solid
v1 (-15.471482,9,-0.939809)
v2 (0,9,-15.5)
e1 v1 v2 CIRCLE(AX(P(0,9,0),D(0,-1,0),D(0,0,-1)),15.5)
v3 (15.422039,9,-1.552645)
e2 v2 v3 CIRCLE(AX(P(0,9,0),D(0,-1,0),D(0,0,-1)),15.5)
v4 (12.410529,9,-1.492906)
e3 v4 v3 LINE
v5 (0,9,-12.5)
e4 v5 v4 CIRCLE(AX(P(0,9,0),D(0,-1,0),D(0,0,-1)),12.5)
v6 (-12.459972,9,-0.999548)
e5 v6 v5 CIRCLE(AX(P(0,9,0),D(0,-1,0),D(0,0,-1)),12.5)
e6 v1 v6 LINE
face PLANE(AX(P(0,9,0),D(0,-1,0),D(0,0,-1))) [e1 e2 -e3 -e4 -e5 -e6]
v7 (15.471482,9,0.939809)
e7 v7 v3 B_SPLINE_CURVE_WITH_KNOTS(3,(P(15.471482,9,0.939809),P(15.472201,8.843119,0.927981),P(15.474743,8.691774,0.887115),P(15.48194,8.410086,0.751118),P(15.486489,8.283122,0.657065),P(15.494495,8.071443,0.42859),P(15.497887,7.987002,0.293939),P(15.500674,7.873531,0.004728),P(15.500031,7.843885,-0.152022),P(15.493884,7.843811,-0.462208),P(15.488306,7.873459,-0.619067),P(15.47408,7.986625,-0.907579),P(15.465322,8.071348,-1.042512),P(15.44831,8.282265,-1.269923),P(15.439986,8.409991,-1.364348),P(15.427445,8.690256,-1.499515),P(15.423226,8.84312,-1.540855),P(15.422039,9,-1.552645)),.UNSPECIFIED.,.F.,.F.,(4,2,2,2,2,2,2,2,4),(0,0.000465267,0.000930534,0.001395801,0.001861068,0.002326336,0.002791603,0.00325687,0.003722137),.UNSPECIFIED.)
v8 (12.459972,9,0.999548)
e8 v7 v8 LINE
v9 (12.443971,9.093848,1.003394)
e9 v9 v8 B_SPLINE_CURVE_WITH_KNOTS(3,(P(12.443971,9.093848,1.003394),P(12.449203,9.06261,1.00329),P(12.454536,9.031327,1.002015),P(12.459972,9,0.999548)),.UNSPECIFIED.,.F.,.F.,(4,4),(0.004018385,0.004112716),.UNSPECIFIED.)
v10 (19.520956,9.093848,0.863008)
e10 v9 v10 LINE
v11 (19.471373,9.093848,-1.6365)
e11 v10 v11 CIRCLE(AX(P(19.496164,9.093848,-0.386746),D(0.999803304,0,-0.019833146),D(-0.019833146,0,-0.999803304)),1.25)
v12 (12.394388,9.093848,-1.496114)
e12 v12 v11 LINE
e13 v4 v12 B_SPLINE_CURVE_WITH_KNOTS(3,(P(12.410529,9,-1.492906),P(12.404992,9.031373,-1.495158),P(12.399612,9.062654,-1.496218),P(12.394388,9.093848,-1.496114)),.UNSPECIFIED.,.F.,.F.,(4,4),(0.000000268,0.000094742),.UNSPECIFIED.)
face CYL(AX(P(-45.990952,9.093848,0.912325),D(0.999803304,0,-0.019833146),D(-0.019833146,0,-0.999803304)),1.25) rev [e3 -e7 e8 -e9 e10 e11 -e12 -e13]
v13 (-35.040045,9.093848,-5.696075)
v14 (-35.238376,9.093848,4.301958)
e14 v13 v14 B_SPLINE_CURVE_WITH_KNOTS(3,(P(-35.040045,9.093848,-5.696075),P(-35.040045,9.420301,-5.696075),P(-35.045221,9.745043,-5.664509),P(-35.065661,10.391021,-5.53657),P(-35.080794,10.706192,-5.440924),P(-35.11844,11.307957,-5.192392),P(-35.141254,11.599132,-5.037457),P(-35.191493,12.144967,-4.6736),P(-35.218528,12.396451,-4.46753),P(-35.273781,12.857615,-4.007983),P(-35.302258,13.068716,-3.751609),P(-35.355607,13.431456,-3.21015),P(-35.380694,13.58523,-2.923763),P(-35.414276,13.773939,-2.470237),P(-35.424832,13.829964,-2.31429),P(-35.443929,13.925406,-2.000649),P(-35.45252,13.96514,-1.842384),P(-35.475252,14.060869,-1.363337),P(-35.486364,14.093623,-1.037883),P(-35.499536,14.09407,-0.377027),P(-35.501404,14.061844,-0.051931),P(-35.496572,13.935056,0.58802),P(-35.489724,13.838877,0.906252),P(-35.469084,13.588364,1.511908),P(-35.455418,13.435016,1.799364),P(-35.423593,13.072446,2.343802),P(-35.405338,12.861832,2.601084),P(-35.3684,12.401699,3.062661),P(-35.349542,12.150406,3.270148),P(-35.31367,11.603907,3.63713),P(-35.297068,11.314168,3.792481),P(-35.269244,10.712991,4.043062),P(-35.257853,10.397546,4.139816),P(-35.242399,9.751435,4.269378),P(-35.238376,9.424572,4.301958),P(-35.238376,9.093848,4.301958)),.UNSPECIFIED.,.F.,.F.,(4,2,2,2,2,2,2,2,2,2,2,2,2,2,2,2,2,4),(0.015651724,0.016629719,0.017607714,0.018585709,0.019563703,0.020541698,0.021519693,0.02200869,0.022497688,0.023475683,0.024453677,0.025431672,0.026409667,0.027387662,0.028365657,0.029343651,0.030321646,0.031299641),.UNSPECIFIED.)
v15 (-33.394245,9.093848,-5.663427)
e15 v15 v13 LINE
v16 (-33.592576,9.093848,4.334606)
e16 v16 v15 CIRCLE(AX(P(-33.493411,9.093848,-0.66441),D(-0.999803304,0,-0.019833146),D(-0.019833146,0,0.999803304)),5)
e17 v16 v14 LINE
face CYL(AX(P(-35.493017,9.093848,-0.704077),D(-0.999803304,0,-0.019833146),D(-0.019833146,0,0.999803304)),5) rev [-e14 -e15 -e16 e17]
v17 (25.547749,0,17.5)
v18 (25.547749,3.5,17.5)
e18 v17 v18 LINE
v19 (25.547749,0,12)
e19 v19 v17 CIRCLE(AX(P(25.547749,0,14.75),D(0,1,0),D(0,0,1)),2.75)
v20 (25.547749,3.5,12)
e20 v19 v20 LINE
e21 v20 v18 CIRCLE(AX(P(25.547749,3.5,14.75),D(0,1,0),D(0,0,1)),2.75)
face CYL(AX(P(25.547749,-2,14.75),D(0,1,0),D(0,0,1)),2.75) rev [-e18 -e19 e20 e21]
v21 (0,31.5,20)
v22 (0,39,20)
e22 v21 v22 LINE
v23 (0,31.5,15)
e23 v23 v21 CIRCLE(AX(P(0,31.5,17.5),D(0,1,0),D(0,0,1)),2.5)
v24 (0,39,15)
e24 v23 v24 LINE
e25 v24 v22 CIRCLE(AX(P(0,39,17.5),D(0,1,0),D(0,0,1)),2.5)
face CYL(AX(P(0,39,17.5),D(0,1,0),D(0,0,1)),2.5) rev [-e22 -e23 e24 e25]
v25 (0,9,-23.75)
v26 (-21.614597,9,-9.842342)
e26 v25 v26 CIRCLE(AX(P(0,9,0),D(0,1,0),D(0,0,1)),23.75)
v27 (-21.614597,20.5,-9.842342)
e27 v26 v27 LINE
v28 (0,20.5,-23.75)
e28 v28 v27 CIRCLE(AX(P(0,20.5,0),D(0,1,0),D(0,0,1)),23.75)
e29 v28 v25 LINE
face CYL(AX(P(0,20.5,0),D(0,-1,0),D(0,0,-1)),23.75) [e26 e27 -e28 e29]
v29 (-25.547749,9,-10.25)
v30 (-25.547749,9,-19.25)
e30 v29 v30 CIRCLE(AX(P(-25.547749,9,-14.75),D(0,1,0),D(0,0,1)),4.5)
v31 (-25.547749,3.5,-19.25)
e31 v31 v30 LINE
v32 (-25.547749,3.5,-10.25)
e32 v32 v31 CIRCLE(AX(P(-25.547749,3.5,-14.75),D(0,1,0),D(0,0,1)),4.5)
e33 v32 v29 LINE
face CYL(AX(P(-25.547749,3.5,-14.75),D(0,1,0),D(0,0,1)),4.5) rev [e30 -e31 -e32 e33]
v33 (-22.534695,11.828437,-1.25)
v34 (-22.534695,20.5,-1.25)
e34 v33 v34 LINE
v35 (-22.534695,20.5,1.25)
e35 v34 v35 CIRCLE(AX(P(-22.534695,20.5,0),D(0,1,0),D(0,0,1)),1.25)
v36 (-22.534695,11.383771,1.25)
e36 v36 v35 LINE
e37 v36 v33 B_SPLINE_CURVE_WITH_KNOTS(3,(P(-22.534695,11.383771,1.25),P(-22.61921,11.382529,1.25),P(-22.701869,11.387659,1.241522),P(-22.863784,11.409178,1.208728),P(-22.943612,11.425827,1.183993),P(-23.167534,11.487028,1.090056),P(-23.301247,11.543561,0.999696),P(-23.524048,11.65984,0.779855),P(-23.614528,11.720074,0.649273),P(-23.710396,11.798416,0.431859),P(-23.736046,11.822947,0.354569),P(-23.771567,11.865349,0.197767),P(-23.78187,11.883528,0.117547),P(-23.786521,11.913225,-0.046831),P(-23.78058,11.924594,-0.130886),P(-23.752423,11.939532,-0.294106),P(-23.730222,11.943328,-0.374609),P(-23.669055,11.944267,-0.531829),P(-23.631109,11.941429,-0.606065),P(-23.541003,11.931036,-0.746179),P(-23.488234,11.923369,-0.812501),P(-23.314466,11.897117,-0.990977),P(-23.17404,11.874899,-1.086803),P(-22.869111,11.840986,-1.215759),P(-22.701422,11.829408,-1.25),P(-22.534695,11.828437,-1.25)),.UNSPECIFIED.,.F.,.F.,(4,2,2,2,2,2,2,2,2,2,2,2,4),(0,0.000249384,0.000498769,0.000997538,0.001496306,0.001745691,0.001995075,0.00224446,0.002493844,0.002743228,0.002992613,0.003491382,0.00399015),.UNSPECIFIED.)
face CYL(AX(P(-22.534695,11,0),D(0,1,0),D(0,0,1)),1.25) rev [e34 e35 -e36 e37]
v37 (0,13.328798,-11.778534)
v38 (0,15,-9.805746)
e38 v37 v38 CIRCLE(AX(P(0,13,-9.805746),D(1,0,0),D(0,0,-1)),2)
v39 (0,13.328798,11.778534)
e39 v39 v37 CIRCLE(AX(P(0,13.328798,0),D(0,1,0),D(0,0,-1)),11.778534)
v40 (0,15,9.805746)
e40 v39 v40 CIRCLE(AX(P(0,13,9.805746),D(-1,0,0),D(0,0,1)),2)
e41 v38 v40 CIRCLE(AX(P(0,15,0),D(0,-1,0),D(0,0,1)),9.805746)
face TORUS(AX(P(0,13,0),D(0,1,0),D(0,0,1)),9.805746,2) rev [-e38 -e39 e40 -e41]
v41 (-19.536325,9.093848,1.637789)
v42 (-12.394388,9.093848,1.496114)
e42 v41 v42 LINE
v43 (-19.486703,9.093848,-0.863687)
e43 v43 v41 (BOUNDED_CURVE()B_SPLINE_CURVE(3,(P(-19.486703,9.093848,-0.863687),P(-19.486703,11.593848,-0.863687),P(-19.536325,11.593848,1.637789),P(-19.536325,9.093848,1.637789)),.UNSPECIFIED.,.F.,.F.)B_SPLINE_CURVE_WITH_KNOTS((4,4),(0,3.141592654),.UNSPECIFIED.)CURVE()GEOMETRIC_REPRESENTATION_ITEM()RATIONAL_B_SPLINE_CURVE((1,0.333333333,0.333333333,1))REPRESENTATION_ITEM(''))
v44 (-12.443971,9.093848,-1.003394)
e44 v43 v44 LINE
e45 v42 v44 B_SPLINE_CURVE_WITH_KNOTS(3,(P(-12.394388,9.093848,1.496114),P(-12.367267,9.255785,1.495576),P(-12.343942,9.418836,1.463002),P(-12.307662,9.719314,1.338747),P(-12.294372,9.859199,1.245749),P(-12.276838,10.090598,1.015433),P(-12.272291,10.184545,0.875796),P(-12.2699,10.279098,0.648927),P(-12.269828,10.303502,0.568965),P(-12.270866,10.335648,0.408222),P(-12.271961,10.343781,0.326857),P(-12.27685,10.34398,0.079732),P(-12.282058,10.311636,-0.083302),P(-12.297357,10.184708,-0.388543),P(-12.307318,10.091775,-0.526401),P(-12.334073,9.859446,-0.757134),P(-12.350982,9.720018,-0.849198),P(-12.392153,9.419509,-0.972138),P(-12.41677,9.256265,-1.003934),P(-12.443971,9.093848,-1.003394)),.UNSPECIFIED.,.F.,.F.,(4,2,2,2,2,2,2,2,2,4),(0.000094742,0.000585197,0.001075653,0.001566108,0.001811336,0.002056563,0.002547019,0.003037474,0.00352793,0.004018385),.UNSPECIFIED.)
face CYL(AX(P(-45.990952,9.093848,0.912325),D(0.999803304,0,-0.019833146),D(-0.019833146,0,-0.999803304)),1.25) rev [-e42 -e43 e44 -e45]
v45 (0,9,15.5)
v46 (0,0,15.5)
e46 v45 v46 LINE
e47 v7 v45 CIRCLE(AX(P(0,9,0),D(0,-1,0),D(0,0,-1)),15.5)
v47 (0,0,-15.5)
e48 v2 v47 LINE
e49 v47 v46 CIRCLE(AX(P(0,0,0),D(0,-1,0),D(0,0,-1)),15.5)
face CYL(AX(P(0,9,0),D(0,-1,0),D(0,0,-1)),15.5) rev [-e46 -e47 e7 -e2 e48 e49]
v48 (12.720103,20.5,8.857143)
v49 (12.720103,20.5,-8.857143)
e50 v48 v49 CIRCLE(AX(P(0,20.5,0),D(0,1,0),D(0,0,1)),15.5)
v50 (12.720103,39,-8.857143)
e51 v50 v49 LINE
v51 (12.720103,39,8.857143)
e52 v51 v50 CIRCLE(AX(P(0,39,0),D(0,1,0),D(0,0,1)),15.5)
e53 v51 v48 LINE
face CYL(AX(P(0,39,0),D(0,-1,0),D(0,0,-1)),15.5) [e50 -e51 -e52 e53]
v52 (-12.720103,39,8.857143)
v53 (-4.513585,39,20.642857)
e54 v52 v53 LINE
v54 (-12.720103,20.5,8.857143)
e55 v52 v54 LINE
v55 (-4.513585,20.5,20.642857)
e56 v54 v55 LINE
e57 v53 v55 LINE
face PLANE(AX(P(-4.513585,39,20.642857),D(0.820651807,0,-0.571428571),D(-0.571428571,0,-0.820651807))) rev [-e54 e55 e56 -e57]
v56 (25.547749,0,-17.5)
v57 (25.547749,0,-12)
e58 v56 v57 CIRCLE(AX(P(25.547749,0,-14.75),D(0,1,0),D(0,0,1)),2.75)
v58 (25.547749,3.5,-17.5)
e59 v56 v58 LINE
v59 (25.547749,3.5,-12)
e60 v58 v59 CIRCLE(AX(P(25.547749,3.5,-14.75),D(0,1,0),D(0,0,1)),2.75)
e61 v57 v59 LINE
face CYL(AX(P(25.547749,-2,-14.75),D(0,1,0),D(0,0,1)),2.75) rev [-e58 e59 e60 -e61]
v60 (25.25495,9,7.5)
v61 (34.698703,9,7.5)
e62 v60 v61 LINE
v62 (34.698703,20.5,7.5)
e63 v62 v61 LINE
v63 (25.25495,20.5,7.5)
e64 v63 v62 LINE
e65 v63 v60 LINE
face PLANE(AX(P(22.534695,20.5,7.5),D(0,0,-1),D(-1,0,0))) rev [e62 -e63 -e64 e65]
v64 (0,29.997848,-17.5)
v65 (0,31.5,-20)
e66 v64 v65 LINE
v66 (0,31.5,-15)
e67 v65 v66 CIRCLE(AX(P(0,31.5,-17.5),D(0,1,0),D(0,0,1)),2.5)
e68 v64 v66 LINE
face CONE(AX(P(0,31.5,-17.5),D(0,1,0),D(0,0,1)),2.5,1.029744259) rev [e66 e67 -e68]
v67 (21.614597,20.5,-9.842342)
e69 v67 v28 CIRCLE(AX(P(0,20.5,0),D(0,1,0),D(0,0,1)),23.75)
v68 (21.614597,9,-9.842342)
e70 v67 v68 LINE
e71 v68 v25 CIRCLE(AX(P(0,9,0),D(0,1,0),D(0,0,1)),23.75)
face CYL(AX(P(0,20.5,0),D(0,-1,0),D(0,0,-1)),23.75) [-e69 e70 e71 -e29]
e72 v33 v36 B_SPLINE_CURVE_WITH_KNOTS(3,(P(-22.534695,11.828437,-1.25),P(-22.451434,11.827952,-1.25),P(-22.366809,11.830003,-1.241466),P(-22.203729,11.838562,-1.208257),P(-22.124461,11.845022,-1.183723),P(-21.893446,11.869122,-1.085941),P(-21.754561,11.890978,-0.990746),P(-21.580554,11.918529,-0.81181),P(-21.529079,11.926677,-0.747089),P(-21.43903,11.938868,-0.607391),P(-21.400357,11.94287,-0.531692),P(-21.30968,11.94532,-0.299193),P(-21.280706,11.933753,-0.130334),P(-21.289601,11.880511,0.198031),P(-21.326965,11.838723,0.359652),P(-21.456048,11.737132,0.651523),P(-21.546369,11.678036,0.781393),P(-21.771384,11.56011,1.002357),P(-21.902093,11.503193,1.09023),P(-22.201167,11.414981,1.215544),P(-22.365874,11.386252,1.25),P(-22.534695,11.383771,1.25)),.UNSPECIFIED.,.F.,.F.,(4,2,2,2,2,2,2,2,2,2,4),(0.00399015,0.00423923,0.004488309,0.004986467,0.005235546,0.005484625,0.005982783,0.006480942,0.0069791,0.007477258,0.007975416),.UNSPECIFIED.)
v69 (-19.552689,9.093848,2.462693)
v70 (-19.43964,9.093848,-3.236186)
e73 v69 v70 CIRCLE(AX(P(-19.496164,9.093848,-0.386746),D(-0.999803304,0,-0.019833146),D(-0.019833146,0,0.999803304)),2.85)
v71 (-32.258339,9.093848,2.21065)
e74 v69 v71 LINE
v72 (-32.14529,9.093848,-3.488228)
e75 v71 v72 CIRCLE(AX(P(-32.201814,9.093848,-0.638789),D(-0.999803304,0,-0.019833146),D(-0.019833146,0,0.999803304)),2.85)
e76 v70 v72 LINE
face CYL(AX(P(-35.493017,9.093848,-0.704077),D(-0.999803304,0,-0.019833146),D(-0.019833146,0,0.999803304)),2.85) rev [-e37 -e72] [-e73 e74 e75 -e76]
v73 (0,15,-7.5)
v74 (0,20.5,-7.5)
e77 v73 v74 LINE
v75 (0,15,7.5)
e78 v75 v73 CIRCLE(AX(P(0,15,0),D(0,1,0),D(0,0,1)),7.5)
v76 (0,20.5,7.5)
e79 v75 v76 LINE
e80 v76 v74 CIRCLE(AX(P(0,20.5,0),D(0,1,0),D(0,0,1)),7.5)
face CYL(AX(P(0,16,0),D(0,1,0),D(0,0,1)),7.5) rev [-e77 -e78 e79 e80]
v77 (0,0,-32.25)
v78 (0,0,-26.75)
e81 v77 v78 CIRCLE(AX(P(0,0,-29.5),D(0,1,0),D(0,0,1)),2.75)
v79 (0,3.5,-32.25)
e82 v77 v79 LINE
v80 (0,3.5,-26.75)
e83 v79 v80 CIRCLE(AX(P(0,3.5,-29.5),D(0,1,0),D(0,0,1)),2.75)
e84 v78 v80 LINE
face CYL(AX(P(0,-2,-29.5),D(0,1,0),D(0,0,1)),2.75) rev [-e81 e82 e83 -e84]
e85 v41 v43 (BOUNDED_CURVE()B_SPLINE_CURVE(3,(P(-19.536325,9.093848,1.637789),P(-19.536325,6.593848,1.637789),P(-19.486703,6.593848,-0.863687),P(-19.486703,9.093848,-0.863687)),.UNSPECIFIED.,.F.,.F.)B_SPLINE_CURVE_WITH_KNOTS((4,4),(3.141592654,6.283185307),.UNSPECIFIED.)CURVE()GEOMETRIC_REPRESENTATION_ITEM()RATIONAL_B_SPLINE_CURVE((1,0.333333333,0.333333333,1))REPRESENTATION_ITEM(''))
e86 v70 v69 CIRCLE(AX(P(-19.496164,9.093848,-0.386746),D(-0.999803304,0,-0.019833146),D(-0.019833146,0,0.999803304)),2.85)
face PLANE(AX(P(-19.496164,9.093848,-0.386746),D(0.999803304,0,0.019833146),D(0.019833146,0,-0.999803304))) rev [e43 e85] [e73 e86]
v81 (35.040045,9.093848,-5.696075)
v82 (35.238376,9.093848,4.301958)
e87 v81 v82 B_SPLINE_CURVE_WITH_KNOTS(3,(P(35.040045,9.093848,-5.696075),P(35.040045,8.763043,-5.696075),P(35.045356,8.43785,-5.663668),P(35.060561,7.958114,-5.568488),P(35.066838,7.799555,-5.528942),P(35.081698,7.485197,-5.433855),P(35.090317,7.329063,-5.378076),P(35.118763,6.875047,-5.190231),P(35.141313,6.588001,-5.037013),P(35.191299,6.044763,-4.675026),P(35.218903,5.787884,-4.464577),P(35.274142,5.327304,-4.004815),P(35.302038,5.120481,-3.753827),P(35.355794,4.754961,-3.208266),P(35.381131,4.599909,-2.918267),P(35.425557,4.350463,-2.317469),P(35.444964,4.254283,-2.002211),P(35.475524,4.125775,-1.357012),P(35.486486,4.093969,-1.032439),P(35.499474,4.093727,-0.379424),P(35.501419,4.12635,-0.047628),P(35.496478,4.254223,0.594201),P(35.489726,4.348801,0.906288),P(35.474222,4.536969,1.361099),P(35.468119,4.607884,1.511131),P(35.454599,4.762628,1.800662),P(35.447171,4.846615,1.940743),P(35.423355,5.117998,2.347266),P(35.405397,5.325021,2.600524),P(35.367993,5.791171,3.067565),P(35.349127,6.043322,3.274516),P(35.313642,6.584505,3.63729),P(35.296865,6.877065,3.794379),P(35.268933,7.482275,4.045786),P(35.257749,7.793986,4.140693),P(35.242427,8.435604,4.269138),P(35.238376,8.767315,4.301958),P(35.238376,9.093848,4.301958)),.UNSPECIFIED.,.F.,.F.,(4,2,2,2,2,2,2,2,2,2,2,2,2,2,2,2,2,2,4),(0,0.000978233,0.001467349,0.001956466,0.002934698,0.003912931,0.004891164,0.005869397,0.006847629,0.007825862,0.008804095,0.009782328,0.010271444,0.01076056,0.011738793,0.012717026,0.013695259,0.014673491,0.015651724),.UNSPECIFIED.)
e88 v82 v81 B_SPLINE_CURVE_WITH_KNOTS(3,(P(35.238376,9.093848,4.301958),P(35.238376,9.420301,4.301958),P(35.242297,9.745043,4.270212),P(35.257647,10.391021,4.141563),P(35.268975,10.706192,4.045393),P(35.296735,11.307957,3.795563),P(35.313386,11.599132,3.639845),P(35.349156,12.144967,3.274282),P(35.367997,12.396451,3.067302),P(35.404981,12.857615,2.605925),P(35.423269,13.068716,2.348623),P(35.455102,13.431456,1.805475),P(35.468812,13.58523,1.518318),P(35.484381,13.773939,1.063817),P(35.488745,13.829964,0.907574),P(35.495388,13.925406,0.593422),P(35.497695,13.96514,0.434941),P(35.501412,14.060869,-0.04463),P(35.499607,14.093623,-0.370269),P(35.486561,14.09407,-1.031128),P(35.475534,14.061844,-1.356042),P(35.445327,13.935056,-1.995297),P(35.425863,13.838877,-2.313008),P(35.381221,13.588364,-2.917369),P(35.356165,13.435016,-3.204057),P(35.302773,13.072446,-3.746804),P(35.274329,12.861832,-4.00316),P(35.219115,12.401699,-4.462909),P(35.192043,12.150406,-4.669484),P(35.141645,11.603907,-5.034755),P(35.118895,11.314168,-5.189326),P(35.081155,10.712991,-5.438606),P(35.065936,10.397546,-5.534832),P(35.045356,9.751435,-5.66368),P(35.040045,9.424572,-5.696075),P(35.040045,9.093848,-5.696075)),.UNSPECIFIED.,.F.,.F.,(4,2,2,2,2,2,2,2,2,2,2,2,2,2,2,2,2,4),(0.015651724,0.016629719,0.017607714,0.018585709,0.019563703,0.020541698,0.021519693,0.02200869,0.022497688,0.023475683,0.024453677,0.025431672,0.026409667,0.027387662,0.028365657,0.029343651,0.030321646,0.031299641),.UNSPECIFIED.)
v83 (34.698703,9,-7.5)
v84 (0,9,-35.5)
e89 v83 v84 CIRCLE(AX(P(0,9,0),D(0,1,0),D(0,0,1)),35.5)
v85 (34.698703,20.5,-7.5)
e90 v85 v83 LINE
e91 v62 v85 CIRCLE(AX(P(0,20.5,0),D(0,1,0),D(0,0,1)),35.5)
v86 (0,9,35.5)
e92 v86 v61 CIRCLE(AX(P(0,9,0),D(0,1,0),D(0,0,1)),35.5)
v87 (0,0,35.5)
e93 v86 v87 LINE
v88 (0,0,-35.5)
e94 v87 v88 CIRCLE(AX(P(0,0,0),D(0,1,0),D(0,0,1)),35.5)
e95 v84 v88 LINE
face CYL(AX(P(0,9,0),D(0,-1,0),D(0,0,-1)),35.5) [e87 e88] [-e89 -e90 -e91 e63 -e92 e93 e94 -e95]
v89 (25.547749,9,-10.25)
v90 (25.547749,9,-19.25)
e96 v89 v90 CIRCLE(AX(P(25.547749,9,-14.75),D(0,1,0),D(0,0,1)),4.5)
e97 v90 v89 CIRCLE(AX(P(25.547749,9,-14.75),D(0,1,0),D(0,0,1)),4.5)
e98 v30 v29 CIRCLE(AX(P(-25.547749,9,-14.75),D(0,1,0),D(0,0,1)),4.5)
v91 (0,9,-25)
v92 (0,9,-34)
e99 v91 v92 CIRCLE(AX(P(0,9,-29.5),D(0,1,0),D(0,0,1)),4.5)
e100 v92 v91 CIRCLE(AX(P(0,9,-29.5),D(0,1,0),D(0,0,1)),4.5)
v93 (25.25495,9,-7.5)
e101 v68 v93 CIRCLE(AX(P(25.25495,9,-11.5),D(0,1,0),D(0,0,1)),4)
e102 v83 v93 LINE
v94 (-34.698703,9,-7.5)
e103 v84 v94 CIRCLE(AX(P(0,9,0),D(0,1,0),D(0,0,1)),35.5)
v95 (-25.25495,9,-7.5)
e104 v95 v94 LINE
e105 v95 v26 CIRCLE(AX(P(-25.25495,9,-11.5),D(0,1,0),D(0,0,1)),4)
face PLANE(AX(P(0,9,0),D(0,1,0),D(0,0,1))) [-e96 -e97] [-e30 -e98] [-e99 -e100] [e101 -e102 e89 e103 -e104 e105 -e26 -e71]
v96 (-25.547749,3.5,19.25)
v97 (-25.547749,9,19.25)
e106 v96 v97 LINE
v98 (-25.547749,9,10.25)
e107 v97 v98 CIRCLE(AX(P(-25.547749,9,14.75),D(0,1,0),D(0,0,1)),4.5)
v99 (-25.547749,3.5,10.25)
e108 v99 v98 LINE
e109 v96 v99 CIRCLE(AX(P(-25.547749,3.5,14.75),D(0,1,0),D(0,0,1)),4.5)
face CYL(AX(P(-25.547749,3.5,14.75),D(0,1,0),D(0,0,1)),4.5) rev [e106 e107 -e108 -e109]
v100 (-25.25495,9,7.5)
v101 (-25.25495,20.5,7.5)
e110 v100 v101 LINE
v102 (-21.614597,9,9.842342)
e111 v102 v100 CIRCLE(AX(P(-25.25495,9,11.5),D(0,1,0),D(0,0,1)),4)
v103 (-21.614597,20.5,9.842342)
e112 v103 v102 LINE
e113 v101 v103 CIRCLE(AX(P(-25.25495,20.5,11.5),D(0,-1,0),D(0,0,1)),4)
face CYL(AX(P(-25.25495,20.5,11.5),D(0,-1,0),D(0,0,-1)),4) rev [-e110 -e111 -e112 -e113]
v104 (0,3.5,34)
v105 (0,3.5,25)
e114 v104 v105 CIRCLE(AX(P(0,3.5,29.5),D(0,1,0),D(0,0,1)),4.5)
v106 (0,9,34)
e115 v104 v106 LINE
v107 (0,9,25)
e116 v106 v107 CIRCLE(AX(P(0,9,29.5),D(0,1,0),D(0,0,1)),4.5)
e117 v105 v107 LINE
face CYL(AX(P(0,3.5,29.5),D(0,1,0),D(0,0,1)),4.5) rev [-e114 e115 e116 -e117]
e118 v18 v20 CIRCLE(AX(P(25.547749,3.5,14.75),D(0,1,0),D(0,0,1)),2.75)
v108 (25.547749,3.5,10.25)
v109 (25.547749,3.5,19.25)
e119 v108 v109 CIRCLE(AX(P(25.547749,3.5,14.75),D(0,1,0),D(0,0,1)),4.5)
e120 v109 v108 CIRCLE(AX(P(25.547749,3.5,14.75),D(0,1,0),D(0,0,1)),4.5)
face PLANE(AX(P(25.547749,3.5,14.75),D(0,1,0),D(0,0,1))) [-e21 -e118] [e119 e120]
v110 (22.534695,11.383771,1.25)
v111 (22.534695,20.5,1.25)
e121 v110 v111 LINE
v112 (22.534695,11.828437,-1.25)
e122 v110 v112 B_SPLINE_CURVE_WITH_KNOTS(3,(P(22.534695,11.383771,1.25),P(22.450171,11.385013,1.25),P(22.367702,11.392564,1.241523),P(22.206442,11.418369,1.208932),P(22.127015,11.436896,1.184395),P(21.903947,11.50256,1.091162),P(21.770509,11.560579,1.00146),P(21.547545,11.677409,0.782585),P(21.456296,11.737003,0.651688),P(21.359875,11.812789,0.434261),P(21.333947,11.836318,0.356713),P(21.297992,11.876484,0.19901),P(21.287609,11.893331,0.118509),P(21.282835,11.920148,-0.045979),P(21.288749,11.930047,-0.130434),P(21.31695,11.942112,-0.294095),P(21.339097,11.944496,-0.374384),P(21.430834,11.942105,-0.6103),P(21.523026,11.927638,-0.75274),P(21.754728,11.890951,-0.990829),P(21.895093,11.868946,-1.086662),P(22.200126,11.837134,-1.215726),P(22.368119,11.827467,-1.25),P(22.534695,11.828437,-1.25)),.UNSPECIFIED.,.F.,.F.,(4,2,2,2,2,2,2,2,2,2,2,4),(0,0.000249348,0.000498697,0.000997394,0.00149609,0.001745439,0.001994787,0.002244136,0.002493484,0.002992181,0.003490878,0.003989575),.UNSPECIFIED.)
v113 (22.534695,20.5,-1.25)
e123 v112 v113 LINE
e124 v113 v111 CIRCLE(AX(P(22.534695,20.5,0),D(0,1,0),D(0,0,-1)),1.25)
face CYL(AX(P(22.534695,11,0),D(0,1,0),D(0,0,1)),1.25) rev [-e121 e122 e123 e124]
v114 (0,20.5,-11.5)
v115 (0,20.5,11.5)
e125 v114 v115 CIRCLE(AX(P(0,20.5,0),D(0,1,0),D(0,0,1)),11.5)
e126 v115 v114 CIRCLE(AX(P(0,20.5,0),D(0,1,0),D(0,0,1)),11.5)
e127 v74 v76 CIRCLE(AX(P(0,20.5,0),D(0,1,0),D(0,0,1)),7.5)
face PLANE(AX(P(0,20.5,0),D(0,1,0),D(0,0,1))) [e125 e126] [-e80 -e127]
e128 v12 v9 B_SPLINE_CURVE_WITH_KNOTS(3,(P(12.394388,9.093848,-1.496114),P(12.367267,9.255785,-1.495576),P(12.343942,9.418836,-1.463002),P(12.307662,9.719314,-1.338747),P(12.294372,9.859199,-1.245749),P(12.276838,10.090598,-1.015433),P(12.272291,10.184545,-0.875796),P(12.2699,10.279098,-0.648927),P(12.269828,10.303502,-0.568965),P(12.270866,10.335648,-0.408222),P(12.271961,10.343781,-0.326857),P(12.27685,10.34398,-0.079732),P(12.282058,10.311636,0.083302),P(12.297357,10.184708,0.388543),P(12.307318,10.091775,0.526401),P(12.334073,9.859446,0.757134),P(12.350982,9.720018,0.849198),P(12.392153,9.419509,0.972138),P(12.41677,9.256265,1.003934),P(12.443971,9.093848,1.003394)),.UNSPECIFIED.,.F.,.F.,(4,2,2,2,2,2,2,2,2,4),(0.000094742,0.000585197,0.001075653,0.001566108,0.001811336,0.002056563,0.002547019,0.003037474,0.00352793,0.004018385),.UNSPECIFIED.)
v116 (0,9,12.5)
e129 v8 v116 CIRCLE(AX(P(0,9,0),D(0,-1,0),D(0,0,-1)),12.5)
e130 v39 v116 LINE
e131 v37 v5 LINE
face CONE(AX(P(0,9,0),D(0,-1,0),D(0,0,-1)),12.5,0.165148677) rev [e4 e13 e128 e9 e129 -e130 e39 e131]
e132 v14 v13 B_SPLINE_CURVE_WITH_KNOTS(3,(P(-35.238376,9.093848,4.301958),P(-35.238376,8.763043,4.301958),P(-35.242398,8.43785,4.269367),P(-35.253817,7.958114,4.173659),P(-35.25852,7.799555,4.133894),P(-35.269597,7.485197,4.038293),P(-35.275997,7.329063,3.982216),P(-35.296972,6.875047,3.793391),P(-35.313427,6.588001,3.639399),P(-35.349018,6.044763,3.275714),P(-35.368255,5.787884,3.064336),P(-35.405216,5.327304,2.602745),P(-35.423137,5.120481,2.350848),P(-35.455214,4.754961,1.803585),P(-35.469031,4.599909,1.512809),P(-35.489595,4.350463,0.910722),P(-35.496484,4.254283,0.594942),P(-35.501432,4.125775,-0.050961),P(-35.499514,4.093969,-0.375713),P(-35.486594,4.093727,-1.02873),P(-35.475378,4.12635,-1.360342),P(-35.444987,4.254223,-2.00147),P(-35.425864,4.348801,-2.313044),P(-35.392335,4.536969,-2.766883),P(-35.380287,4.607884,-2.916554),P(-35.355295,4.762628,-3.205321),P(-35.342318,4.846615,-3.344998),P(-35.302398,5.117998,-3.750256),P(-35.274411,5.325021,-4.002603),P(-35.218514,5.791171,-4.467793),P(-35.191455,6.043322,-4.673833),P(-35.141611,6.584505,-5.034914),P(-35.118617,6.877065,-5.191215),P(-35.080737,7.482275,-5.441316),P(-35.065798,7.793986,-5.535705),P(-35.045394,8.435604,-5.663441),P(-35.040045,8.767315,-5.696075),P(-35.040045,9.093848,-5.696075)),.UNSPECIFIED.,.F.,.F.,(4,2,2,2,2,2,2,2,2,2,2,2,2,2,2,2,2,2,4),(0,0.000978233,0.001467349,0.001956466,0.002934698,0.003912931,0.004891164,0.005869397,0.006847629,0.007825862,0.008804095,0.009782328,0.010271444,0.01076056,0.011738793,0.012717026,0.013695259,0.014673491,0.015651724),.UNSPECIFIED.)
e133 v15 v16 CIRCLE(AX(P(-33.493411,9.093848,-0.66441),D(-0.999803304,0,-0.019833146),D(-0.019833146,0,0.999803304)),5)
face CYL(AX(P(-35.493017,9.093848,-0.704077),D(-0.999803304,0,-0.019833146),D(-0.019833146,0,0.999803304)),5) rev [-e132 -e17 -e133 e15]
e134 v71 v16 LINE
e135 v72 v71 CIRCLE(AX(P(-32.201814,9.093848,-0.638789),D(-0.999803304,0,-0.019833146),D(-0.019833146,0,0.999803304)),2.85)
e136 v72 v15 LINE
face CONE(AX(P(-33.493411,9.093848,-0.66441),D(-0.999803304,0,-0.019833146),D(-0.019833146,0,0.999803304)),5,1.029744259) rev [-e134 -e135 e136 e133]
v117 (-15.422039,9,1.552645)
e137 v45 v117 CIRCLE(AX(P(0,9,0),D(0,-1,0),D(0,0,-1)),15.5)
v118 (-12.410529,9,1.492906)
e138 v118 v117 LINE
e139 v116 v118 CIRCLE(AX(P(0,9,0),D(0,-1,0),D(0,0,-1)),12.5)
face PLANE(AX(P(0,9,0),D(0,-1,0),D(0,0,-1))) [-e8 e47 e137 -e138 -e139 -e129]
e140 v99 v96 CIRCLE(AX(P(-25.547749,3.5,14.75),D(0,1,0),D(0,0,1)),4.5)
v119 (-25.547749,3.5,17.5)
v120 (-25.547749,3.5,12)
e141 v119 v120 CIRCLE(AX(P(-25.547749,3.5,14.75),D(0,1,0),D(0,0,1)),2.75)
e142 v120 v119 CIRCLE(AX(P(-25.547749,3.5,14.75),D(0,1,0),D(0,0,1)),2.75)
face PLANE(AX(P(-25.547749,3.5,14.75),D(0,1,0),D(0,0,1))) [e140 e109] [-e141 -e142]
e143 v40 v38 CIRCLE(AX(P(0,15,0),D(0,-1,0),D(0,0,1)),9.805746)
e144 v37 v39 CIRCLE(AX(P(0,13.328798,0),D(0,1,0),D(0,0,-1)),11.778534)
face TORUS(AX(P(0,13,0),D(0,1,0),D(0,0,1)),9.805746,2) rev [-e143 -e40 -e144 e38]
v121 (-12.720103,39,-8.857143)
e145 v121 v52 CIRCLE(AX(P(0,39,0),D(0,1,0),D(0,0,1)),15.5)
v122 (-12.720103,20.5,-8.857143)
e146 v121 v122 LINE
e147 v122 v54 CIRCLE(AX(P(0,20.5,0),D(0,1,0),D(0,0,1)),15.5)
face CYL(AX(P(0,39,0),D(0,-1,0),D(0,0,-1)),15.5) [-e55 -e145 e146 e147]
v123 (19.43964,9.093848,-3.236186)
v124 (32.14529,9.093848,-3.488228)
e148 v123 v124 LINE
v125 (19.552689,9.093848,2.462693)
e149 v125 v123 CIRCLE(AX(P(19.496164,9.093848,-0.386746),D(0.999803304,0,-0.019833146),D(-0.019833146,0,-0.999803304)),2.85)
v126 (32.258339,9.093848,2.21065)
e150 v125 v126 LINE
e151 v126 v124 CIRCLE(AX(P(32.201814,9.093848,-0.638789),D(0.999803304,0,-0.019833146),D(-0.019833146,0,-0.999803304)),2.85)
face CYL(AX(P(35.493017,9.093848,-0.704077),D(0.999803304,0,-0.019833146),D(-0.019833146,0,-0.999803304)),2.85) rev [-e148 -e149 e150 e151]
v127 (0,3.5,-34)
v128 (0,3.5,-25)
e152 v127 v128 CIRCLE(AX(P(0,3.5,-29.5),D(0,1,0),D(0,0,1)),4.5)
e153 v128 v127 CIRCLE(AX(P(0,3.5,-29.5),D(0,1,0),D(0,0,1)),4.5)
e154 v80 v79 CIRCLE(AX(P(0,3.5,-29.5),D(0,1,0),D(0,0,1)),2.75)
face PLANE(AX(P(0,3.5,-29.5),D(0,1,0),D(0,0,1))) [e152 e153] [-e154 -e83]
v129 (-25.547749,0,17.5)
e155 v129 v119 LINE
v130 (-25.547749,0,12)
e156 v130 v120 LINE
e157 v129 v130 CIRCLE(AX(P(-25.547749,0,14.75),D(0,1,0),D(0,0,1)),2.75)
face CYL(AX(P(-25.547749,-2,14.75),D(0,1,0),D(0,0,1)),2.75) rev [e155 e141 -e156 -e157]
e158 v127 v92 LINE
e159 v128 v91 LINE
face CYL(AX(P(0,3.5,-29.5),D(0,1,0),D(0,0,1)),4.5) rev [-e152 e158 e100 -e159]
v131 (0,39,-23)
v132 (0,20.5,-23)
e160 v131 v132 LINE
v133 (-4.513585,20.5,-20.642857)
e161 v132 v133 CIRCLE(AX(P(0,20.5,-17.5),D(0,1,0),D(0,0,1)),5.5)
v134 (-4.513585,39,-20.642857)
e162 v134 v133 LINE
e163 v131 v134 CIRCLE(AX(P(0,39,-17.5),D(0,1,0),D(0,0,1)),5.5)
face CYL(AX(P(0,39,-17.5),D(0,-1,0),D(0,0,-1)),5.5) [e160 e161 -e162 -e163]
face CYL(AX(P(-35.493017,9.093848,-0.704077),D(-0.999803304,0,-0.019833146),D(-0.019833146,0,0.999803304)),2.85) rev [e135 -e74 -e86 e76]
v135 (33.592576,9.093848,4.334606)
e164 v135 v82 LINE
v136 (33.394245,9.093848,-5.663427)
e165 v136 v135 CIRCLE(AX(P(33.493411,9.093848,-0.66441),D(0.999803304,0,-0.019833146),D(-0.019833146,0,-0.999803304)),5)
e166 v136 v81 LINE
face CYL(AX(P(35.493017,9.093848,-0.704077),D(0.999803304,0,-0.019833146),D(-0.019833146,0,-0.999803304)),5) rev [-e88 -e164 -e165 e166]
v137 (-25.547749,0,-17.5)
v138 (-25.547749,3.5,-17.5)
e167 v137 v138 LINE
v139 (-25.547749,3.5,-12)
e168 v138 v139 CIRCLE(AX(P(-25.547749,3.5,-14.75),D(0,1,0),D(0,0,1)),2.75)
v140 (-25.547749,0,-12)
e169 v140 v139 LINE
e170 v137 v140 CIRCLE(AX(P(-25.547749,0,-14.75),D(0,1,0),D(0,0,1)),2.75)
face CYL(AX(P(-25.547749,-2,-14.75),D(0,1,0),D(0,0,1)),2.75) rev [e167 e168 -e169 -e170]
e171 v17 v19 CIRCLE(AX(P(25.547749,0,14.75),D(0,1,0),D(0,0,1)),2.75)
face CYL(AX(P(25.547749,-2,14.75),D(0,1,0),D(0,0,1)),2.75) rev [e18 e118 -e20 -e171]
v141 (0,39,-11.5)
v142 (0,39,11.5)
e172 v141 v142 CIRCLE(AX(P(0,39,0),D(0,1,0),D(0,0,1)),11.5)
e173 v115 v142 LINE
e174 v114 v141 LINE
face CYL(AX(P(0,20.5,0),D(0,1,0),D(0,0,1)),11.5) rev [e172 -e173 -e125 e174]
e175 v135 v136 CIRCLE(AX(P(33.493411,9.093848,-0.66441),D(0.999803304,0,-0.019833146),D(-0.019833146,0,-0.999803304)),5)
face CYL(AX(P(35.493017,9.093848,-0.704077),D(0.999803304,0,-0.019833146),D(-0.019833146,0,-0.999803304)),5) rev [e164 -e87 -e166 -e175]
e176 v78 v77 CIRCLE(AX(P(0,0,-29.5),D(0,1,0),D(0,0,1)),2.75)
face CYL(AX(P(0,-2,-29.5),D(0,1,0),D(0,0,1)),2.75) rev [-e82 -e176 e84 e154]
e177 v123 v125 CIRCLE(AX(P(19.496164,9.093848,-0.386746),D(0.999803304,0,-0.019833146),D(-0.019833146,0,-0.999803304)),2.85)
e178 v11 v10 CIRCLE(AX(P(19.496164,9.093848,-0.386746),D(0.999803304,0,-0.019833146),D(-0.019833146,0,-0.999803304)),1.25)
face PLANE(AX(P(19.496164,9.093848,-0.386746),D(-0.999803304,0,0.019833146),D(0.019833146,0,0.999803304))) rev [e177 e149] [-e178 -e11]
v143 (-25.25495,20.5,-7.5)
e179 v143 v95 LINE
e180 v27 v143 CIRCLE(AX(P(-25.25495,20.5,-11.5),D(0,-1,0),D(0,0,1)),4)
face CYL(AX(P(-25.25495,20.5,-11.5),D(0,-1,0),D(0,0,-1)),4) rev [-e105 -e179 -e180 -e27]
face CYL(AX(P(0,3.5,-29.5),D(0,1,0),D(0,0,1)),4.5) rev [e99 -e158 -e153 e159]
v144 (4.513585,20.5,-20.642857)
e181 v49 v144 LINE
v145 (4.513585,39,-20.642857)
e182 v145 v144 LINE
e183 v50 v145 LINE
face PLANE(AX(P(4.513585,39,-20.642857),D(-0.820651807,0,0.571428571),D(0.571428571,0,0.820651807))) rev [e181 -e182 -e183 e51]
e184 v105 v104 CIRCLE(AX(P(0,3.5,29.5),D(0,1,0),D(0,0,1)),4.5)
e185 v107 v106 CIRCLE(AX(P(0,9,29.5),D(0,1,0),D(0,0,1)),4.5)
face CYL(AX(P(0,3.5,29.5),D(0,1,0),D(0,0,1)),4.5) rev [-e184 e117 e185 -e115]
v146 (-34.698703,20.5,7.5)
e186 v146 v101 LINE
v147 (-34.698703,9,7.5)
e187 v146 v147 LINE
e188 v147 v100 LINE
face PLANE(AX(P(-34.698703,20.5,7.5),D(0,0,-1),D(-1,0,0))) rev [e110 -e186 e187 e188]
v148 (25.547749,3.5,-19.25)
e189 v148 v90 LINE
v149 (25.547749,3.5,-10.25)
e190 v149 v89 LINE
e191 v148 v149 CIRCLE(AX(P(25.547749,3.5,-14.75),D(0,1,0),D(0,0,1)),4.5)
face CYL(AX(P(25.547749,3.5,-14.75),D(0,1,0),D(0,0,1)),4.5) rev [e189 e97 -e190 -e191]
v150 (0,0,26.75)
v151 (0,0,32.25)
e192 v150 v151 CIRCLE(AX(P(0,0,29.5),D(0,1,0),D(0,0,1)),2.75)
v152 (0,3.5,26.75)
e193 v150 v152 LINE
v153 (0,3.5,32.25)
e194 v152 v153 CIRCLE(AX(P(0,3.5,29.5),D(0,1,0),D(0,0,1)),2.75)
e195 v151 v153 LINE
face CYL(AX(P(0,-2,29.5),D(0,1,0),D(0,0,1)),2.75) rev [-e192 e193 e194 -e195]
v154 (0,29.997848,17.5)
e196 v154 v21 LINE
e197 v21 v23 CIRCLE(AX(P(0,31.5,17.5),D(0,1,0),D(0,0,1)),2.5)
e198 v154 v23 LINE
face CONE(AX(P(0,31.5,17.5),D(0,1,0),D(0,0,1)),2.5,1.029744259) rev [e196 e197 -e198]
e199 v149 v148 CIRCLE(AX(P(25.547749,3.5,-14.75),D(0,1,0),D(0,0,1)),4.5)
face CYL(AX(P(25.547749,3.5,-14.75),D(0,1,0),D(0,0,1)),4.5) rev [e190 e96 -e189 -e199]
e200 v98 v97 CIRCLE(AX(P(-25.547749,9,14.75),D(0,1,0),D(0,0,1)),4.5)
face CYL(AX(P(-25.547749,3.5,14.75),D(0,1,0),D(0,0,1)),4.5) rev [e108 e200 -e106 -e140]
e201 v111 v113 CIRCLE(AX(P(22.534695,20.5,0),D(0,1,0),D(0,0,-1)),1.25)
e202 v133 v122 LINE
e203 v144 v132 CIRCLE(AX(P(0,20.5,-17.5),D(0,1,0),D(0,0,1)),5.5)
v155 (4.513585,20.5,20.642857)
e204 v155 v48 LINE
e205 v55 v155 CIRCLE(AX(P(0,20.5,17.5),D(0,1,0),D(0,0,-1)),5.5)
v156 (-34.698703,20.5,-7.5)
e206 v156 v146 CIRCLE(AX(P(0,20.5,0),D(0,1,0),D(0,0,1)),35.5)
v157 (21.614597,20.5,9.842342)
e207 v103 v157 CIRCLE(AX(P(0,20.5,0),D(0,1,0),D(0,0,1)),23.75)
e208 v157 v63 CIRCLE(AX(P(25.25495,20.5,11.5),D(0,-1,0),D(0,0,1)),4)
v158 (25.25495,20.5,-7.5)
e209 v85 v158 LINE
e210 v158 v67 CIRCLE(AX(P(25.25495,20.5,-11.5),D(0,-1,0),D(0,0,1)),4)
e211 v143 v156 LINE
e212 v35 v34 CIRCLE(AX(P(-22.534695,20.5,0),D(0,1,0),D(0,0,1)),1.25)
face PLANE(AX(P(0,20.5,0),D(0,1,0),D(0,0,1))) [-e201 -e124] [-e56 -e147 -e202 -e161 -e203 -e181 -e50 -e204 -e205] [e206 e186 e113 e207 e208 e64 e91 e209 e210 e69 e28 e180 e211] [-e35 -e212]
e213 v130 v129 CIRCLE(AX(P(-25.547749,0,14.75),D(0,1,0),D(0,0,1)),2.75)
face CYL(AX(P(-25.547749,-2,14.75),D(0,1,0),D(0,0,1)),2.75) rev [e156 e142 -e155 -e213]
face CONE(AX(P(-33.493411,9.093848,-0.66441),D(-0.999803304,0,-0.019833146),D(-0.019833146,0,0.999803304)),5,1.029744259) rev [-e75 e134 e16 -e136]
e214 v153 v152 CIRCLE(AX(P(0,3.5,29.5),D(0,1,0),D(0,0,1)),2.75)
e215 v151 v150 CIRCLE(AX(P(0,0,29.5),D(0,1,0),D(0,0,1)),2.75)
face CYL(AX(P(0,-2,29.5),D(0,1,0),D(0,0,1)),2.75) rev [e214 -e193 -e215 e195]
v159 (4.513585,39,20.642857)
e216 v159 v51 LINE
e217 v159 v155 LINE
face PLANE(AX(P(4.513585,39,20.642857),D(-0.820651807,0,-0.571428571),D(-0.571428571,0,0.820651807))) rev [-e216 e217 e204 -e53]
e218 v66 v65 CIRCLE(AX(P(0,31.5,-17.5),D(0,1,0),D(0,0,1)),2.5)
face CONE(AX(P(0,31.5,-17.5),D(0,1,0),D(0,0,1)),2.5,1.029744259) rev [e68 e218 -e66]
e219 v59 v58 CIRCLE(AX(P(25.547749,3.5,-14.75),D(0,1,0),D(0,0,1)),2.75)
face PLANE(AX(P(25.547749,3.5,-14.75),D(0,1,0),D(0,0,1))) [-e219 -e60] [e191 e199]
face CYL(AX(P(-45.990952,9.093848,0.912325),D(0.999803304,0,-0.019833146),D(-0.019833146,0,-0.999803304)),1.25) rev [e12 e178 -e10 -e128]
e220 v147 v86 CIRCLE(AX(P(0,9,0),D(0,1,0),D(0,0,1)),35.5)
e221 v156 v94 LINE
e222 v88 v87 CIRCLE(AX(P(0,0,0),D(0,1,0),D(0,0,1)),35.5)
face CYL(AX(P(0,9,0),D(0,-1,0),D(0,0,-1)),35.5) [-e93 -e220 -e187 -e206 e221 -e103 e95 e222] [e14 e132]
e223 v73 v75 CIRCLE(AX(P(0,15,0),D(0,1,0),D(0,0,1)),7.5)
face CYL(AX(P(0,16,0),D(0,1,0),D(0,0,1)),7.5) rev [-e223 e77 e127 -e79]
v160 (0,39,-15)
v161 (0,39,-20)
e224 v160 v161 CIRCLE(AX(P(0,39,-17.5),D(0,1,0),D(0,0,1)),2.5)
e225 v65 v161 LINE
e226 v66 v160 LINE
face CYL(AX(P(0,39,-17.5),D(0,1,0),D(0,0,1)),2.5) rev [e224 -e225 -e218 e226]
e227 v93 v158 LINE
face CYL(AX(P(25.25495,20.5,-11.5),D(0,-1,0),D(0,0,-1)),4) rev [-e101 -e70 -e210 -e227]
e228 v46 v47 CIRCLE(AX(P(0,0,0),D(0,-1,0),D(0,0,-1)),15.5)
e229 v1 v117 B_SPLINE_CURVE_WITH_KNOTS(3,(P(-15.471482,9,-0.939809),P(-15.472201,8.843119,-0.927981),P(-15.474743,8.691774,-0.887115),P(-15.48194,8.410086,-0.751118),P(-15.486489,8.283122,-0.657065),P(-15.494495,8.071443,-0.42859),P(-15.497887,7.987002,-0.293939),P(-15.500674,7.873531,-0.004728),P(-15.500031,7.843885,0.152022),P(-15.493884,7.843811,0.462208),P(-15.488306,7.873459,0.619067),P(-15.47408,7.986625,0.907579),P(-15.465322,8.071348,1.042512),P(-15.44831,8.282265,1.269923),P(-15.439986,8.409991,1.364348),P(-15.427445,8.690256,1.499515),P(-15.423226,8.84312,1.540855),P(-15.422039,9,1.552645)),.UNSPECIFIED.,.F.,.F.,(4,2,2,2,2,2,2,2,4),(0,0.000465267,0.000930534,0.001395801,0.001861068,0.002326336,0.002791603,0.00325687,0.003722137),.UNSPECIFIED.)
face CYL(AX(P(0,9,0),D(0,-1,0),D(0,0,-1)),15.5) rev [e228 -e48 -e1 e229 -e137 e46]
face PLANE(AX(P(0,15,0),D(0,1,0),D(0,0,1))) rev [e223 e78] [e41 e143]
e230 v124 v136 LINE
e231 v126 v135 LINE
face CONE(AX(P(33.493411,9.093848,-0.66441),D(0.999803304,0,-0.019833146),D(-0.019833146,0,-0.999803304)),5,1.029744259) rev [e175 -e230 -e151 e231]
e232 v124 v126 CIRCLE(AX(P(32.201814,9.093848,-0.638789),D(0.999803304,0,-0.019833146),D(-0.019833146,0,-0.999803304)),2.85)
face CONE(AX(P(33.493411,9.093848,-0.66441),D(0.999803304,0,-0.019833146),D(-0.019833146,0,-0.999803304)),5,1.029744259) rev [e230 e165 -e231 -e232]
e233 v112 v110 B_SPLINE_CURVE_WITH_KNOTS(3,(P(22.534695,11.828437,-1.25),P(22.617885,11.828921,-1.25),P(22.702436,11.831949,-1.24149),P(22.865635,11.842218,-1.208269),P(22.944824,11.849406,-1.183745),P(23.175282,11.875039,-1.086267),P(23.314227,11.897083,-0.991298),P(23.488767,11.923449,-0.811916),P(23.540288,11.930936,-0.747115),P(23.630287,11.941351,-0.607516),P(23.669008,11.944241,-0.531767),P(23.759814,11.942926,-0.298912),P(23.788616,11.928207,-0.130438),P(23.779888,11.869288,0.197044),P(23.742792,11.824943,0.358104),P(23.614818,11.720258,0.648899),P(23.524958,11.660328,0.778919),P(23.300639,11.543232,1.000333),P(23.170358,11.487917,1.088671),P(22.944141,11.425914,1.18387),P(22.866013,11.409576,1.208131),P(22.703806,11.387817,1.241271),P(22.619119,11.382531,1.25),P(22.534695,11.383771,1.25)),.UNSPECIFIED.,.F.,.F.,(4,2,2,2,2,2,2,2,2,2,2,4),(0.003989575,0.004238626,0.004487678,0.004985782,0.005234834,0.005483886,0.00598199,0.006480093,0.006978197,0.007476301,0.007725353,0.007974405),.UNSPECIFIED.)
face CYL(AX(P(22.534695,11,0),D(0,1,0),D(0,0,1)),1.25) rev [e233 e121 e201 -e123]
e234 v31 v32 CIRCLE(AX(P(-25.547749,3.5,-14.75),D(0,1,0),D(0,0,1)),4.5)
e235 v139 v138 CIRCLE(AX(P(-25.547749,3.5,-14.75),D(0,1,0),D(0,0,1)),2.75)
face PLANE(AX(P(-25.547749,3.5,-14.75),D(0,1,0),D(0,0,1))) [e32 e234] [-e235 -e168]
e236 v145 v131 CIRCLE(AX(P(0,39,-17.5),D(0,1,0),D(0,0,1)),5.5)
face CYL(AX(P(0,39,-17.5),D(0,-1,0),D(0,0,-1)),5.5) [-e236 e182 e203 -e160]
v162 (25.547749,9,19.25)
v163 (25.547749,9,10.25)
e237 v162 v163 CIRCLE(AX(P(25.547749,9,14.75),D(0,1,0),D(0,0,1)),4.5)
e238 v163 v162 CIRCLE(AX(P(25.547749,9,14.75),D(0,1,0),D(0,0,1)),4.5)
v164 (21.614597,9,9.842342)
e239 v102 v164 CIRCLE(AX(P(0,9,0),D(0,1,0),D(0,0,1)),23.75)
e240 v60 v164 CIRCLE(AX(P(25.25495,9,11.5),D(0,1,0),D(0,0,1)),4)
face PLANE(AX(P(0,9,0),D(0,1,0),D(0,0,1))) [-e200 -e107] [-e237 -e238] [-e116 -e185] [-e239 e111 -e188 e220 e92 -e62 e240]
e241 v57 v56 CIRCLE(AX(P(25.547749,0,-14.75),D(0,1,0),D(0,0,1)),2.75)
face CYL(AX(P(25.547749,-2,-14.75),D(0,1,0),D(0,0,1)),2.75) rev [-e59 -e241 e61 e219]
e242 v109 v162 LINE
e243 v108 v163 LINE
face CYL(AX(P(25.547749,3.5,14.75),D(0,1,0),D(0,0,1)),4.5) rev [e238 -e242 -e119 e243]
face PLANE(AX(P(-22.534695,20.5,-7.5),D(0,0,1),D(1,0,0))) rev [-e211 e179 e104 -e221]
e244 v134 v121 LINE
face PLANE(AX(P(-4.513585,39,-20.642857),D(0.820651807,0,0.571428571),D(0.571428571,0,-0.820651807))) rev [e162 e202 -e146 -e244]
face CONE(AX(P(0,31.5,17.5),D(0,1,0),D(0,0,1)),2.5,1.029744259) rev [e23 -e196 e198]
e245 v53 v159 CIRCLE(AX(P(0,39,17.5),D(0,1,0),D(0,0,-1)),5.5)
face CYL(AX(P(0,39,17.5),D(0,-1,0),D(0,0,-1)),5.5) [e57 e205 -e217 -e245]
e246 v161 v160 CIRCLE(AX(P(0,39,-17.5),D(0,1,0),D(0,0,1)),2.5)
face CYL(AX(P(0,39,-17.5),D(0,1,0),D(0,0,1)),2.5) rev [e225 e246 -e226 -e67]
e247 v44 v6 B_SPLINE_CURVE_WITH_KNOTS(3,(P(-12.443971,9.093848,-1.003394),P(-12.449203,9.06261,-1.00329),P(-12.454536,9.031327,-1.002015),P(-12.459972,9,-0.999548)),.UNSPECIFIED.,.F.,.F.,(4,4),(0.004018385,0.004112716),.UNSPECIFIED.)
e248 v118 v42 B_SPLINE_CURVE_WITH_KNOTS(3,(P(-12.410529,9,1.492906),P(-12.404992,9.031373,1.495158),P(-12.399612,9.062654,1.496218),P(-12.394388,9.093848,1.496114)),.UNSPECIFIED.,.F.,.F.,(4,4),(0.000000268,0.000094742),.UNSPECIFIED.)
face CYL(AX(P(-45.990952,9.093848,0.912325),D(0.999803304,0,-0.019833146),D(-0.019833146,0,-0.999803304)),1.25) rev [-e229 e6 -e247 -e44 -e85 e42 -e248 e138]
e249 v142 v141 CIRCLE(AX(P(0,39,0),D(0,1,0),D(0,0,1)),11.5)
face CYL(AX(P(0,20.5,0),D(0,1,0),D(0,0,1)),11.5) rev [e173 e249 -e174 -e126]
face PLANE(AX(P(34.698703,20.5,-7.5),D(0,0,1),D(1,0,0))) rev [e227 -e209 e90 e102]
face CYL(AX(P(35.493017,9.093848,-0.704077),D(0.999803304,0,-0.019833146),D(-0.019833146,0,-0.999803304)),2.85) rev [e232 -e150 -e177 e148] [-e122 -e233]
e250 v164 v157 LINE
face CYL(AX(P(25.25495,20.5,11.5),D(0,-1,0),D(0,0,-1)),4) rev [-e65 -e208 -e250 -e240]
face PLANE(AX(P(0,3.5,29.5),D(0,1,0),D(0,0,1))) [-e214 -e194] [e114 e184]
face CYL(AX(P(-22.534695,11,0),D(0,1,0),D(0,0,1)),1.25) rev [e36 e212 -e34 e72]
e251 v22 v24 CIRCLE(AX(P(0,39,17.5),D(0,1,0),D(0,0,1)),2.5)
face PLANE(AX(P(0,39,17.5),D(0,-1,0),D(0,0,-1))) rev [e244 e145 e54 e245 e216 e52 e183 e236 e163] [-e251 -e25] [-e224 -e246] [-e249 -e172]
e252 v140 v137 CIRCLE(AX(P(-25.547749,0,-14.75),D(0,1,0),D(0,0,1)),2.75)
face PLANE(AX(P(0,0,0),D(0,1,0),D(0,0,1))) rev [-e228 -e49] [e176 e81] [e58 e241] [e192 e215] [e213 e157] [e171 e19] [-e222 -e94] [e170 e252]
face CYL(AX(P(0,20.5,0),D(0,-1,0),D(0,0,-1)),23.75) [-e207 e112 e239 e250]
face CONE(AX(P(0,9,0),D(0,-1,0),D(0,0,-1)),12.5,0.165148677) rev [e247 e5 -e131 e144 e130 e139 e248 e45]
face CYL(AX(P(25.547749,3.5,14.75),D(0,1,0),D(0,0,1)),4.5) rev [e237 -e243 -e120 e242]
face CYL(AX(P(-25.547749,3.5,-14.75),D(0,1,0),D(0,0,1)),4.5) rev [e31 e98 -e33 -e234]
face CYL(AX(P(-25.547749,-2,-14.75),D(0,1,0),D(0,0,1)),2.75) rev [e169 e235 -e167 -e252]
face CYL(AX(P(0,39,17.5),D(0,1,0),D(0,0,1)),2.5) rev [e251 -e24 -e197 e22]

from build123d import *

# Parameters (mm, degrees)
BASE_FLANGE_SKETCH_R           = 35.5
BASE_FLANGE_71_DEPTH           = 9
HUB_BOSS_DEPTH                 = 11.5
OVAL_TOP_BOSS_DEPTH            = 18.5
CENTRAL_BORE_SKETCH_R          = 11.5
CENTRAL_BORE_23_DEPTH          = 18.5
UNDERSIDE_RECESS_SKETCH_R      = 15.5
UNDERSIDE_RECESS_31_DEPTH      = 9
BORE_STEP_SKETCH_R             = 7.5
BORE_STEP_15_DEPTH             = 4.5
BORE_RELIEF_SKETCH_R           = 7.5
BORE_RELIEF_CUT_DEPTH          = 4.5
BORE_EDGE_FILLET_R2_R          = 2
DOWEL_HOLES_5_D                = 5
DOWEL_HOLES_5_DEPTH            = 7.5
DOWEL_HOLES_5_TIP              = 1.502151548
FLANGE_COUNTERBORE_SKETCH_R    = 4.5
FLANGE_COUNTERBORES_6X_9_DEPTH = 5.5
FLANGE_BOLT_HOLE_SKETCH_R      = 2.75
FLANGE_BOLT_HOLES_6X_5_5_DEPTH = 5.5
HUB_PIN_HOLES_SKETCH_R         = 1.25
HUB_PIN_HOLES_DEPTH            = 9.5
CROSS_DRILL_SKETCH_R           = 1.25
CROSS_DRILL_2_5_DEPTH          = 65.5
HUB_FILLET_R4_R                = 4


with BuildPart() as part:
    # Base Flange Sketch → Base Flange _71 (new body)
    with BuildSketch(Plane(origin=(0, 0, 0), x_dir=(1, 0, 0), z_dir=(0, 1, 0))):
        with Locations(Location((0, 0, 0), (0, 0, 270))):
            Circle(BASE_FLANGE_SKETCH_R)
    extrude(amount=BASE_FLANGE_71_DEPTH)

    # Hub Profile Sketch → Hub Boss (add)
    with BuildSketch(Plane(origin=(0, 9, 0), x_dir=(1, 0, 0), z_dir=(0, 1, 0))):
        with BuildLine():
            Line((-22.534695472, 7.5), (-34.698703146, 7.5))
            ThreePointArc((-34.698703146, 7.5), (-35.5, 0), (-34.698703146, -7.5))
            Line((-34.698703146, -7.5), (-22.534695472, -7.5))
            ThreePointArc((-22.534695472, -7.5), (0, -23.75), (22.534695472, -7.5))
            Line((22.534695472, -7.5), (34.698703146, -7.5))
            ThreePointArc((34.698703146, -7.5), (35.5, 0), (34.698703146, 7.5))
            Line((34.698703146, 7.5), (22.534695472, 7.5))
            ThreePointArc((22.534695472, 7.5), (0, 23.75), (-22.534695472, 7.5))
        make_face()
    extrude(amount=HUB_BOSS_DEPTH)

    # Oval Top Boss Sketch → Oval Top Boss (add)
    with BuildSketch(Plane(origin=(0, 20.5, 0), x_dir=(1, 0, 0), z_dir=(0, 1, 0))):
        with BuildLine():
            Line((-4.513584937, 20.642857143), (-12.720103003, 8.857142857))
            ThreePointArc((-12.720103003, 8.857142857), (-15.5, 0), (-12.720103003, -8.857142857))
            Line((-12.720103003, -8.857142857), (-4.513584937, -20.642857143))
            ThreePointArc((-4.513584937, -20.642857143), (0, -23), (4.513584937, -20.642857143))
            Line((4.513584937, -20.642857143), (12.720103003, -8.857142857))
            ThreePointArc((12.720103003, -8.857142857), (15.5, 0), (12.720103003, 8.857142857))
            Line((12.720103003, 8.857142857), (4.513584937, 20.642857143))
            ThreePointArc((4.513584937, 20.642857143), (0, 23), (-4.513584937, 20.642857143))
        make_face()
    extrude(amount=OVAL_TOP_BOSS_DEPTH)

    # Central Bore Sketch → Central Bore _23 (cut)
    with BuildSketch(Plane(origin=(0, 39, 0), x_dir=(1, 0, 0), z_dir=(0, 1, 0))):
        with Locations(Location((0, 0, 0), (0, 0, 270))):
            Circle(CENTRAL_BORE_SKETCH_R)
    extrude(amount=-CENTRAL_BORE_23_DEPTH, mode=Mode.SUBTRACT)

    # Underside Recess Sketch → Underside Recess _31 (cut)
    with BuildSketch(Plane.XZ):
        with Locations(Location((0, 0, 0), (0, 0, 270))):
            Circle(UNDERSIDE_RECESS_SKETCH_R)
    extrude(amount=-UNDERSIDE_RECESS_31_DEPTH, mode=Mode.SUBTRACT)

    # Bore Step Sketch → Bore Step _15 (cut)
    with BuildSketch(Plane(origin=(0, 20.5, 0), x_dir=(1, 0, 0), z_dir=(0, 1, 0))):
        with Locations(Location((0, 0, 0), (0, 0, 270))):
            Circle(BORE_STEP_SKETCH_R)
    extrude(amount=-BORE_STEP_15_DEPTH, mode=Mode.SUBTRACT)

    # Sketch11 → Threaded Bore _25 (revolve, cut)
    with BuildSketch(Plane(origin=(0, 9, 0), x_dir=(0, 0, -1), z_dir=(1, 0, 0))):
        Polygon((0, 0), (0, 6), (11.5, 6), (12.5, 0), align=None)
    revolve(axis=Axis((0, 119, 0), (0, -1, 0)), mode=Mode.SUBTRACT)

    # Bore Relief Sketch → Bore Relief Cut (cut)
    with BuildSketch(Plane(origin=(0, 16, 0), x_dir=(1, 0, 0), z_dir=(0, 1, 0))):
        with Locations(Location((0, 0, 0), (0, 0, 270))):
            Circle(BORE_RELIEF_SKETCH_R)
    extrude(amount=-BORE_RELIEF_CUT_DEPTH, mode=Mode.SUBTRACT)

    # Bore Edge Fillet R2
    bore_edge_fillet_r2_edges = [part.edges().sort_by_distance(p)[0] for p in [
        (0, 15, 11.5),
    ]]
    fillet(bore_edge_fillet_r2_edges, radius=BORE_EDGE_FILLET_R2_R)

    # Dowel Holes _5
    with Locations(Plane(origin=(0, 39, 0), x_dir=(1, 0, 0), z_dir=(0, 1, 0))):
        with Locations((0, 17.5), (0, -17.5)):
            Hole(DOWEL_HOLES_5_D / 2, depth=DOWEL_HOLES_5_DEPTH)
            with Locations((0, 0, -(DOWEL_HOLES_5_DEPTH + DOWEL_HOLES_5_TIP / 2))):  # 118° drill point
                Cone(0, DOWEL_HOLES_5_D / 2, DOWEL_HOLES_5_TIP, mode=Mode.SUBTRACT)

    # Flange Counterbore Sketch → Flange Counterbores 6x_9 (cut)
    with BuildSketch(Plane(origin=(0, 9, 0), x_dir=(1, 0, 0), z_dir=(0, 1, 0))):
        with Locations(Location((0, 29.5, 0), (0, 0, 270))):
            Circle(FLANGE_COUNTERBORE_SKETCH_R)
        with Locations(Location((25.547749412, 14.75, 0), (0, 0, 270))):
            Circle(FLANGE_COUNTERBORE_SKETCH_R)
        with Locations(Location((25.547749412, -14.75, 0), (0, 0, 270))):
            Circle(FLANGE_COUNTERBORE_SKETCH_R)
        with Locations(Location((0, -29.5, 0), (0, 0, 270))):
            Circle(FLANGE_COUNTERBORE_SKETCH_R)
        with Locations(Location((-25.547749412, -14.75, 0), (0, 0, 270))):
            Circle(FLANGE_COUNTERBORE_SKETCH_R)
        with Locations(Location((-25.547749412, 14.75, 0), (0, 0, 270))):
            Circle(FLANGE_COUNTERBORE_SKETCH_R)
    extrude(amount=-FLANGE_COUNTERBORES_6X_9_DEPTH, mode=Mode.SUBTRACT)

    # Flange Bolt Hole Sketch → Flange Bolt Holes 6x_5.5 (cut)
    with BuildSketch(Plane(origin=(0, 3.5, 0), x_dir=(1, 0, 0), z_dir=(0, 1, 0))):
        with Locations(Location((0, 29.5, 0), (0, 0, 270))):
            Circle(FLANGE_BOLT_HOLE_SKETCH_R)
        with Locations(Location((25.547749412, 14.75, 0), (0, 0, 270))):
            Circle(FLANGE_BOLT_HOLE_SKETCH_R)
        with Locations(Location((25.547749412, -14.75, 0), (0, 0, 270))):
            Circle(FLANGE_BOLT_HOLE_SKETCH_R)
        with Locations(Location((0, -29.5, 0), (0, 0, 270))):
            Circle(FLANGE_BOLT_HOLE_SKETCH_R)
        with Locations(Location((-25.547749412, -14.75, 0), (0, 0, 270))):
            Circle(FLANGE_BOLT_HOLE_SKETCH_R)
        with Locations(Location((-25.547749412, 14.75, 0), (0, 0, 270))):
            Circle(FLANGE_BOLT_HOLE_SKETCH_R)
    extrude(amount=-FLANGE_BOLT_HOLES_6X_5_5_DEPTH, mode=Mode.SUBTRACT)

    # Hub Pin Holes Sketch → Hub Pin Holes (cut)
    with BuildSketch(Plane(origin=(0, 20.5, 0), x_dir=(1, 0, 0), z_dir=(0, 1, 0))):
        with Locations(Location((-22.534695472, 0, 0), (0, 0, 270))):
            Circle(HUB_PIN_HOLES_SKETCH_R)
        with Locations(Location((22.534695472, 0, 0), (0, 0, 90))):
            Circle(HUB_PIN_HOLES_SKETCH_R)
    extrude(amount=-HUB_PIN_HOLES_DEPTH, mode=Mode.SUBTRACT)

    # Sketch22 → Side Port _5.7 Counterbored (revolve, cut)
    with BuildSketch(Plane(origin=(-35.493017285, 9.093847626, -0.704076681), x_dir=(-0.0198331459501574, 0, 0.9998033038161656), z_dir=(0, 1, 0))):
        Polygon((0, 0), (0, 16), (2.85, 16), (2.85, 3.291850331), (5, 2), (5, 0), align=None)
    side_port_5_7_counterbored = revolve(axis=Axis((-41.621835432, 9.093847626, -0.82565434), (0.9998033038161656, 0, 0.019833145950157397)), mode=Mode.SUBTRACT)

    # Side Port Mirror: Side Port _5.7 Counterbored across plane
    add(side_port_5_7_counterbored.mirror(Plane(origin=(0, 0, 0), x_dir=(0, 0, 1), z_dir=(1, 0, 0))), mode=Mode.SUBTRACT)

    # Cross Drill Sketch → Cross Drill _2.5 (cut)
    with BuildSketch(Plane(origin=(19.496164424, 0, -0.386746346), x_dir=(-0.019833145950157404, 0, -0.9998033038161656), z_dir=(0.9998033038161657, 0, -0.019833145950157404))):
        with Locations((0, 9.093847626)):
            Circle(CROSS_DRILL_SKETCH_R)
    extrude(amount=-CROSS_DRILL_2_5_DEPTH, mode=Mode.SUBTRACT)

    # Hub Fillet R4
    hub_fillet_r4_edges = [part.edges().sort_by_distance(p)[0] for p in [
        (-22.534695472, 14.75, 7.5),
        (22.534695472, 14.75, 7.5),
        (22.534695472, 14.75, -7.5),
        (-22.534695472, 14.75, -7.5),
    ]]
    fillet(hub_fillet_r4_edges, radius=HUB_FILLET_R4_R)


solid = part.part
